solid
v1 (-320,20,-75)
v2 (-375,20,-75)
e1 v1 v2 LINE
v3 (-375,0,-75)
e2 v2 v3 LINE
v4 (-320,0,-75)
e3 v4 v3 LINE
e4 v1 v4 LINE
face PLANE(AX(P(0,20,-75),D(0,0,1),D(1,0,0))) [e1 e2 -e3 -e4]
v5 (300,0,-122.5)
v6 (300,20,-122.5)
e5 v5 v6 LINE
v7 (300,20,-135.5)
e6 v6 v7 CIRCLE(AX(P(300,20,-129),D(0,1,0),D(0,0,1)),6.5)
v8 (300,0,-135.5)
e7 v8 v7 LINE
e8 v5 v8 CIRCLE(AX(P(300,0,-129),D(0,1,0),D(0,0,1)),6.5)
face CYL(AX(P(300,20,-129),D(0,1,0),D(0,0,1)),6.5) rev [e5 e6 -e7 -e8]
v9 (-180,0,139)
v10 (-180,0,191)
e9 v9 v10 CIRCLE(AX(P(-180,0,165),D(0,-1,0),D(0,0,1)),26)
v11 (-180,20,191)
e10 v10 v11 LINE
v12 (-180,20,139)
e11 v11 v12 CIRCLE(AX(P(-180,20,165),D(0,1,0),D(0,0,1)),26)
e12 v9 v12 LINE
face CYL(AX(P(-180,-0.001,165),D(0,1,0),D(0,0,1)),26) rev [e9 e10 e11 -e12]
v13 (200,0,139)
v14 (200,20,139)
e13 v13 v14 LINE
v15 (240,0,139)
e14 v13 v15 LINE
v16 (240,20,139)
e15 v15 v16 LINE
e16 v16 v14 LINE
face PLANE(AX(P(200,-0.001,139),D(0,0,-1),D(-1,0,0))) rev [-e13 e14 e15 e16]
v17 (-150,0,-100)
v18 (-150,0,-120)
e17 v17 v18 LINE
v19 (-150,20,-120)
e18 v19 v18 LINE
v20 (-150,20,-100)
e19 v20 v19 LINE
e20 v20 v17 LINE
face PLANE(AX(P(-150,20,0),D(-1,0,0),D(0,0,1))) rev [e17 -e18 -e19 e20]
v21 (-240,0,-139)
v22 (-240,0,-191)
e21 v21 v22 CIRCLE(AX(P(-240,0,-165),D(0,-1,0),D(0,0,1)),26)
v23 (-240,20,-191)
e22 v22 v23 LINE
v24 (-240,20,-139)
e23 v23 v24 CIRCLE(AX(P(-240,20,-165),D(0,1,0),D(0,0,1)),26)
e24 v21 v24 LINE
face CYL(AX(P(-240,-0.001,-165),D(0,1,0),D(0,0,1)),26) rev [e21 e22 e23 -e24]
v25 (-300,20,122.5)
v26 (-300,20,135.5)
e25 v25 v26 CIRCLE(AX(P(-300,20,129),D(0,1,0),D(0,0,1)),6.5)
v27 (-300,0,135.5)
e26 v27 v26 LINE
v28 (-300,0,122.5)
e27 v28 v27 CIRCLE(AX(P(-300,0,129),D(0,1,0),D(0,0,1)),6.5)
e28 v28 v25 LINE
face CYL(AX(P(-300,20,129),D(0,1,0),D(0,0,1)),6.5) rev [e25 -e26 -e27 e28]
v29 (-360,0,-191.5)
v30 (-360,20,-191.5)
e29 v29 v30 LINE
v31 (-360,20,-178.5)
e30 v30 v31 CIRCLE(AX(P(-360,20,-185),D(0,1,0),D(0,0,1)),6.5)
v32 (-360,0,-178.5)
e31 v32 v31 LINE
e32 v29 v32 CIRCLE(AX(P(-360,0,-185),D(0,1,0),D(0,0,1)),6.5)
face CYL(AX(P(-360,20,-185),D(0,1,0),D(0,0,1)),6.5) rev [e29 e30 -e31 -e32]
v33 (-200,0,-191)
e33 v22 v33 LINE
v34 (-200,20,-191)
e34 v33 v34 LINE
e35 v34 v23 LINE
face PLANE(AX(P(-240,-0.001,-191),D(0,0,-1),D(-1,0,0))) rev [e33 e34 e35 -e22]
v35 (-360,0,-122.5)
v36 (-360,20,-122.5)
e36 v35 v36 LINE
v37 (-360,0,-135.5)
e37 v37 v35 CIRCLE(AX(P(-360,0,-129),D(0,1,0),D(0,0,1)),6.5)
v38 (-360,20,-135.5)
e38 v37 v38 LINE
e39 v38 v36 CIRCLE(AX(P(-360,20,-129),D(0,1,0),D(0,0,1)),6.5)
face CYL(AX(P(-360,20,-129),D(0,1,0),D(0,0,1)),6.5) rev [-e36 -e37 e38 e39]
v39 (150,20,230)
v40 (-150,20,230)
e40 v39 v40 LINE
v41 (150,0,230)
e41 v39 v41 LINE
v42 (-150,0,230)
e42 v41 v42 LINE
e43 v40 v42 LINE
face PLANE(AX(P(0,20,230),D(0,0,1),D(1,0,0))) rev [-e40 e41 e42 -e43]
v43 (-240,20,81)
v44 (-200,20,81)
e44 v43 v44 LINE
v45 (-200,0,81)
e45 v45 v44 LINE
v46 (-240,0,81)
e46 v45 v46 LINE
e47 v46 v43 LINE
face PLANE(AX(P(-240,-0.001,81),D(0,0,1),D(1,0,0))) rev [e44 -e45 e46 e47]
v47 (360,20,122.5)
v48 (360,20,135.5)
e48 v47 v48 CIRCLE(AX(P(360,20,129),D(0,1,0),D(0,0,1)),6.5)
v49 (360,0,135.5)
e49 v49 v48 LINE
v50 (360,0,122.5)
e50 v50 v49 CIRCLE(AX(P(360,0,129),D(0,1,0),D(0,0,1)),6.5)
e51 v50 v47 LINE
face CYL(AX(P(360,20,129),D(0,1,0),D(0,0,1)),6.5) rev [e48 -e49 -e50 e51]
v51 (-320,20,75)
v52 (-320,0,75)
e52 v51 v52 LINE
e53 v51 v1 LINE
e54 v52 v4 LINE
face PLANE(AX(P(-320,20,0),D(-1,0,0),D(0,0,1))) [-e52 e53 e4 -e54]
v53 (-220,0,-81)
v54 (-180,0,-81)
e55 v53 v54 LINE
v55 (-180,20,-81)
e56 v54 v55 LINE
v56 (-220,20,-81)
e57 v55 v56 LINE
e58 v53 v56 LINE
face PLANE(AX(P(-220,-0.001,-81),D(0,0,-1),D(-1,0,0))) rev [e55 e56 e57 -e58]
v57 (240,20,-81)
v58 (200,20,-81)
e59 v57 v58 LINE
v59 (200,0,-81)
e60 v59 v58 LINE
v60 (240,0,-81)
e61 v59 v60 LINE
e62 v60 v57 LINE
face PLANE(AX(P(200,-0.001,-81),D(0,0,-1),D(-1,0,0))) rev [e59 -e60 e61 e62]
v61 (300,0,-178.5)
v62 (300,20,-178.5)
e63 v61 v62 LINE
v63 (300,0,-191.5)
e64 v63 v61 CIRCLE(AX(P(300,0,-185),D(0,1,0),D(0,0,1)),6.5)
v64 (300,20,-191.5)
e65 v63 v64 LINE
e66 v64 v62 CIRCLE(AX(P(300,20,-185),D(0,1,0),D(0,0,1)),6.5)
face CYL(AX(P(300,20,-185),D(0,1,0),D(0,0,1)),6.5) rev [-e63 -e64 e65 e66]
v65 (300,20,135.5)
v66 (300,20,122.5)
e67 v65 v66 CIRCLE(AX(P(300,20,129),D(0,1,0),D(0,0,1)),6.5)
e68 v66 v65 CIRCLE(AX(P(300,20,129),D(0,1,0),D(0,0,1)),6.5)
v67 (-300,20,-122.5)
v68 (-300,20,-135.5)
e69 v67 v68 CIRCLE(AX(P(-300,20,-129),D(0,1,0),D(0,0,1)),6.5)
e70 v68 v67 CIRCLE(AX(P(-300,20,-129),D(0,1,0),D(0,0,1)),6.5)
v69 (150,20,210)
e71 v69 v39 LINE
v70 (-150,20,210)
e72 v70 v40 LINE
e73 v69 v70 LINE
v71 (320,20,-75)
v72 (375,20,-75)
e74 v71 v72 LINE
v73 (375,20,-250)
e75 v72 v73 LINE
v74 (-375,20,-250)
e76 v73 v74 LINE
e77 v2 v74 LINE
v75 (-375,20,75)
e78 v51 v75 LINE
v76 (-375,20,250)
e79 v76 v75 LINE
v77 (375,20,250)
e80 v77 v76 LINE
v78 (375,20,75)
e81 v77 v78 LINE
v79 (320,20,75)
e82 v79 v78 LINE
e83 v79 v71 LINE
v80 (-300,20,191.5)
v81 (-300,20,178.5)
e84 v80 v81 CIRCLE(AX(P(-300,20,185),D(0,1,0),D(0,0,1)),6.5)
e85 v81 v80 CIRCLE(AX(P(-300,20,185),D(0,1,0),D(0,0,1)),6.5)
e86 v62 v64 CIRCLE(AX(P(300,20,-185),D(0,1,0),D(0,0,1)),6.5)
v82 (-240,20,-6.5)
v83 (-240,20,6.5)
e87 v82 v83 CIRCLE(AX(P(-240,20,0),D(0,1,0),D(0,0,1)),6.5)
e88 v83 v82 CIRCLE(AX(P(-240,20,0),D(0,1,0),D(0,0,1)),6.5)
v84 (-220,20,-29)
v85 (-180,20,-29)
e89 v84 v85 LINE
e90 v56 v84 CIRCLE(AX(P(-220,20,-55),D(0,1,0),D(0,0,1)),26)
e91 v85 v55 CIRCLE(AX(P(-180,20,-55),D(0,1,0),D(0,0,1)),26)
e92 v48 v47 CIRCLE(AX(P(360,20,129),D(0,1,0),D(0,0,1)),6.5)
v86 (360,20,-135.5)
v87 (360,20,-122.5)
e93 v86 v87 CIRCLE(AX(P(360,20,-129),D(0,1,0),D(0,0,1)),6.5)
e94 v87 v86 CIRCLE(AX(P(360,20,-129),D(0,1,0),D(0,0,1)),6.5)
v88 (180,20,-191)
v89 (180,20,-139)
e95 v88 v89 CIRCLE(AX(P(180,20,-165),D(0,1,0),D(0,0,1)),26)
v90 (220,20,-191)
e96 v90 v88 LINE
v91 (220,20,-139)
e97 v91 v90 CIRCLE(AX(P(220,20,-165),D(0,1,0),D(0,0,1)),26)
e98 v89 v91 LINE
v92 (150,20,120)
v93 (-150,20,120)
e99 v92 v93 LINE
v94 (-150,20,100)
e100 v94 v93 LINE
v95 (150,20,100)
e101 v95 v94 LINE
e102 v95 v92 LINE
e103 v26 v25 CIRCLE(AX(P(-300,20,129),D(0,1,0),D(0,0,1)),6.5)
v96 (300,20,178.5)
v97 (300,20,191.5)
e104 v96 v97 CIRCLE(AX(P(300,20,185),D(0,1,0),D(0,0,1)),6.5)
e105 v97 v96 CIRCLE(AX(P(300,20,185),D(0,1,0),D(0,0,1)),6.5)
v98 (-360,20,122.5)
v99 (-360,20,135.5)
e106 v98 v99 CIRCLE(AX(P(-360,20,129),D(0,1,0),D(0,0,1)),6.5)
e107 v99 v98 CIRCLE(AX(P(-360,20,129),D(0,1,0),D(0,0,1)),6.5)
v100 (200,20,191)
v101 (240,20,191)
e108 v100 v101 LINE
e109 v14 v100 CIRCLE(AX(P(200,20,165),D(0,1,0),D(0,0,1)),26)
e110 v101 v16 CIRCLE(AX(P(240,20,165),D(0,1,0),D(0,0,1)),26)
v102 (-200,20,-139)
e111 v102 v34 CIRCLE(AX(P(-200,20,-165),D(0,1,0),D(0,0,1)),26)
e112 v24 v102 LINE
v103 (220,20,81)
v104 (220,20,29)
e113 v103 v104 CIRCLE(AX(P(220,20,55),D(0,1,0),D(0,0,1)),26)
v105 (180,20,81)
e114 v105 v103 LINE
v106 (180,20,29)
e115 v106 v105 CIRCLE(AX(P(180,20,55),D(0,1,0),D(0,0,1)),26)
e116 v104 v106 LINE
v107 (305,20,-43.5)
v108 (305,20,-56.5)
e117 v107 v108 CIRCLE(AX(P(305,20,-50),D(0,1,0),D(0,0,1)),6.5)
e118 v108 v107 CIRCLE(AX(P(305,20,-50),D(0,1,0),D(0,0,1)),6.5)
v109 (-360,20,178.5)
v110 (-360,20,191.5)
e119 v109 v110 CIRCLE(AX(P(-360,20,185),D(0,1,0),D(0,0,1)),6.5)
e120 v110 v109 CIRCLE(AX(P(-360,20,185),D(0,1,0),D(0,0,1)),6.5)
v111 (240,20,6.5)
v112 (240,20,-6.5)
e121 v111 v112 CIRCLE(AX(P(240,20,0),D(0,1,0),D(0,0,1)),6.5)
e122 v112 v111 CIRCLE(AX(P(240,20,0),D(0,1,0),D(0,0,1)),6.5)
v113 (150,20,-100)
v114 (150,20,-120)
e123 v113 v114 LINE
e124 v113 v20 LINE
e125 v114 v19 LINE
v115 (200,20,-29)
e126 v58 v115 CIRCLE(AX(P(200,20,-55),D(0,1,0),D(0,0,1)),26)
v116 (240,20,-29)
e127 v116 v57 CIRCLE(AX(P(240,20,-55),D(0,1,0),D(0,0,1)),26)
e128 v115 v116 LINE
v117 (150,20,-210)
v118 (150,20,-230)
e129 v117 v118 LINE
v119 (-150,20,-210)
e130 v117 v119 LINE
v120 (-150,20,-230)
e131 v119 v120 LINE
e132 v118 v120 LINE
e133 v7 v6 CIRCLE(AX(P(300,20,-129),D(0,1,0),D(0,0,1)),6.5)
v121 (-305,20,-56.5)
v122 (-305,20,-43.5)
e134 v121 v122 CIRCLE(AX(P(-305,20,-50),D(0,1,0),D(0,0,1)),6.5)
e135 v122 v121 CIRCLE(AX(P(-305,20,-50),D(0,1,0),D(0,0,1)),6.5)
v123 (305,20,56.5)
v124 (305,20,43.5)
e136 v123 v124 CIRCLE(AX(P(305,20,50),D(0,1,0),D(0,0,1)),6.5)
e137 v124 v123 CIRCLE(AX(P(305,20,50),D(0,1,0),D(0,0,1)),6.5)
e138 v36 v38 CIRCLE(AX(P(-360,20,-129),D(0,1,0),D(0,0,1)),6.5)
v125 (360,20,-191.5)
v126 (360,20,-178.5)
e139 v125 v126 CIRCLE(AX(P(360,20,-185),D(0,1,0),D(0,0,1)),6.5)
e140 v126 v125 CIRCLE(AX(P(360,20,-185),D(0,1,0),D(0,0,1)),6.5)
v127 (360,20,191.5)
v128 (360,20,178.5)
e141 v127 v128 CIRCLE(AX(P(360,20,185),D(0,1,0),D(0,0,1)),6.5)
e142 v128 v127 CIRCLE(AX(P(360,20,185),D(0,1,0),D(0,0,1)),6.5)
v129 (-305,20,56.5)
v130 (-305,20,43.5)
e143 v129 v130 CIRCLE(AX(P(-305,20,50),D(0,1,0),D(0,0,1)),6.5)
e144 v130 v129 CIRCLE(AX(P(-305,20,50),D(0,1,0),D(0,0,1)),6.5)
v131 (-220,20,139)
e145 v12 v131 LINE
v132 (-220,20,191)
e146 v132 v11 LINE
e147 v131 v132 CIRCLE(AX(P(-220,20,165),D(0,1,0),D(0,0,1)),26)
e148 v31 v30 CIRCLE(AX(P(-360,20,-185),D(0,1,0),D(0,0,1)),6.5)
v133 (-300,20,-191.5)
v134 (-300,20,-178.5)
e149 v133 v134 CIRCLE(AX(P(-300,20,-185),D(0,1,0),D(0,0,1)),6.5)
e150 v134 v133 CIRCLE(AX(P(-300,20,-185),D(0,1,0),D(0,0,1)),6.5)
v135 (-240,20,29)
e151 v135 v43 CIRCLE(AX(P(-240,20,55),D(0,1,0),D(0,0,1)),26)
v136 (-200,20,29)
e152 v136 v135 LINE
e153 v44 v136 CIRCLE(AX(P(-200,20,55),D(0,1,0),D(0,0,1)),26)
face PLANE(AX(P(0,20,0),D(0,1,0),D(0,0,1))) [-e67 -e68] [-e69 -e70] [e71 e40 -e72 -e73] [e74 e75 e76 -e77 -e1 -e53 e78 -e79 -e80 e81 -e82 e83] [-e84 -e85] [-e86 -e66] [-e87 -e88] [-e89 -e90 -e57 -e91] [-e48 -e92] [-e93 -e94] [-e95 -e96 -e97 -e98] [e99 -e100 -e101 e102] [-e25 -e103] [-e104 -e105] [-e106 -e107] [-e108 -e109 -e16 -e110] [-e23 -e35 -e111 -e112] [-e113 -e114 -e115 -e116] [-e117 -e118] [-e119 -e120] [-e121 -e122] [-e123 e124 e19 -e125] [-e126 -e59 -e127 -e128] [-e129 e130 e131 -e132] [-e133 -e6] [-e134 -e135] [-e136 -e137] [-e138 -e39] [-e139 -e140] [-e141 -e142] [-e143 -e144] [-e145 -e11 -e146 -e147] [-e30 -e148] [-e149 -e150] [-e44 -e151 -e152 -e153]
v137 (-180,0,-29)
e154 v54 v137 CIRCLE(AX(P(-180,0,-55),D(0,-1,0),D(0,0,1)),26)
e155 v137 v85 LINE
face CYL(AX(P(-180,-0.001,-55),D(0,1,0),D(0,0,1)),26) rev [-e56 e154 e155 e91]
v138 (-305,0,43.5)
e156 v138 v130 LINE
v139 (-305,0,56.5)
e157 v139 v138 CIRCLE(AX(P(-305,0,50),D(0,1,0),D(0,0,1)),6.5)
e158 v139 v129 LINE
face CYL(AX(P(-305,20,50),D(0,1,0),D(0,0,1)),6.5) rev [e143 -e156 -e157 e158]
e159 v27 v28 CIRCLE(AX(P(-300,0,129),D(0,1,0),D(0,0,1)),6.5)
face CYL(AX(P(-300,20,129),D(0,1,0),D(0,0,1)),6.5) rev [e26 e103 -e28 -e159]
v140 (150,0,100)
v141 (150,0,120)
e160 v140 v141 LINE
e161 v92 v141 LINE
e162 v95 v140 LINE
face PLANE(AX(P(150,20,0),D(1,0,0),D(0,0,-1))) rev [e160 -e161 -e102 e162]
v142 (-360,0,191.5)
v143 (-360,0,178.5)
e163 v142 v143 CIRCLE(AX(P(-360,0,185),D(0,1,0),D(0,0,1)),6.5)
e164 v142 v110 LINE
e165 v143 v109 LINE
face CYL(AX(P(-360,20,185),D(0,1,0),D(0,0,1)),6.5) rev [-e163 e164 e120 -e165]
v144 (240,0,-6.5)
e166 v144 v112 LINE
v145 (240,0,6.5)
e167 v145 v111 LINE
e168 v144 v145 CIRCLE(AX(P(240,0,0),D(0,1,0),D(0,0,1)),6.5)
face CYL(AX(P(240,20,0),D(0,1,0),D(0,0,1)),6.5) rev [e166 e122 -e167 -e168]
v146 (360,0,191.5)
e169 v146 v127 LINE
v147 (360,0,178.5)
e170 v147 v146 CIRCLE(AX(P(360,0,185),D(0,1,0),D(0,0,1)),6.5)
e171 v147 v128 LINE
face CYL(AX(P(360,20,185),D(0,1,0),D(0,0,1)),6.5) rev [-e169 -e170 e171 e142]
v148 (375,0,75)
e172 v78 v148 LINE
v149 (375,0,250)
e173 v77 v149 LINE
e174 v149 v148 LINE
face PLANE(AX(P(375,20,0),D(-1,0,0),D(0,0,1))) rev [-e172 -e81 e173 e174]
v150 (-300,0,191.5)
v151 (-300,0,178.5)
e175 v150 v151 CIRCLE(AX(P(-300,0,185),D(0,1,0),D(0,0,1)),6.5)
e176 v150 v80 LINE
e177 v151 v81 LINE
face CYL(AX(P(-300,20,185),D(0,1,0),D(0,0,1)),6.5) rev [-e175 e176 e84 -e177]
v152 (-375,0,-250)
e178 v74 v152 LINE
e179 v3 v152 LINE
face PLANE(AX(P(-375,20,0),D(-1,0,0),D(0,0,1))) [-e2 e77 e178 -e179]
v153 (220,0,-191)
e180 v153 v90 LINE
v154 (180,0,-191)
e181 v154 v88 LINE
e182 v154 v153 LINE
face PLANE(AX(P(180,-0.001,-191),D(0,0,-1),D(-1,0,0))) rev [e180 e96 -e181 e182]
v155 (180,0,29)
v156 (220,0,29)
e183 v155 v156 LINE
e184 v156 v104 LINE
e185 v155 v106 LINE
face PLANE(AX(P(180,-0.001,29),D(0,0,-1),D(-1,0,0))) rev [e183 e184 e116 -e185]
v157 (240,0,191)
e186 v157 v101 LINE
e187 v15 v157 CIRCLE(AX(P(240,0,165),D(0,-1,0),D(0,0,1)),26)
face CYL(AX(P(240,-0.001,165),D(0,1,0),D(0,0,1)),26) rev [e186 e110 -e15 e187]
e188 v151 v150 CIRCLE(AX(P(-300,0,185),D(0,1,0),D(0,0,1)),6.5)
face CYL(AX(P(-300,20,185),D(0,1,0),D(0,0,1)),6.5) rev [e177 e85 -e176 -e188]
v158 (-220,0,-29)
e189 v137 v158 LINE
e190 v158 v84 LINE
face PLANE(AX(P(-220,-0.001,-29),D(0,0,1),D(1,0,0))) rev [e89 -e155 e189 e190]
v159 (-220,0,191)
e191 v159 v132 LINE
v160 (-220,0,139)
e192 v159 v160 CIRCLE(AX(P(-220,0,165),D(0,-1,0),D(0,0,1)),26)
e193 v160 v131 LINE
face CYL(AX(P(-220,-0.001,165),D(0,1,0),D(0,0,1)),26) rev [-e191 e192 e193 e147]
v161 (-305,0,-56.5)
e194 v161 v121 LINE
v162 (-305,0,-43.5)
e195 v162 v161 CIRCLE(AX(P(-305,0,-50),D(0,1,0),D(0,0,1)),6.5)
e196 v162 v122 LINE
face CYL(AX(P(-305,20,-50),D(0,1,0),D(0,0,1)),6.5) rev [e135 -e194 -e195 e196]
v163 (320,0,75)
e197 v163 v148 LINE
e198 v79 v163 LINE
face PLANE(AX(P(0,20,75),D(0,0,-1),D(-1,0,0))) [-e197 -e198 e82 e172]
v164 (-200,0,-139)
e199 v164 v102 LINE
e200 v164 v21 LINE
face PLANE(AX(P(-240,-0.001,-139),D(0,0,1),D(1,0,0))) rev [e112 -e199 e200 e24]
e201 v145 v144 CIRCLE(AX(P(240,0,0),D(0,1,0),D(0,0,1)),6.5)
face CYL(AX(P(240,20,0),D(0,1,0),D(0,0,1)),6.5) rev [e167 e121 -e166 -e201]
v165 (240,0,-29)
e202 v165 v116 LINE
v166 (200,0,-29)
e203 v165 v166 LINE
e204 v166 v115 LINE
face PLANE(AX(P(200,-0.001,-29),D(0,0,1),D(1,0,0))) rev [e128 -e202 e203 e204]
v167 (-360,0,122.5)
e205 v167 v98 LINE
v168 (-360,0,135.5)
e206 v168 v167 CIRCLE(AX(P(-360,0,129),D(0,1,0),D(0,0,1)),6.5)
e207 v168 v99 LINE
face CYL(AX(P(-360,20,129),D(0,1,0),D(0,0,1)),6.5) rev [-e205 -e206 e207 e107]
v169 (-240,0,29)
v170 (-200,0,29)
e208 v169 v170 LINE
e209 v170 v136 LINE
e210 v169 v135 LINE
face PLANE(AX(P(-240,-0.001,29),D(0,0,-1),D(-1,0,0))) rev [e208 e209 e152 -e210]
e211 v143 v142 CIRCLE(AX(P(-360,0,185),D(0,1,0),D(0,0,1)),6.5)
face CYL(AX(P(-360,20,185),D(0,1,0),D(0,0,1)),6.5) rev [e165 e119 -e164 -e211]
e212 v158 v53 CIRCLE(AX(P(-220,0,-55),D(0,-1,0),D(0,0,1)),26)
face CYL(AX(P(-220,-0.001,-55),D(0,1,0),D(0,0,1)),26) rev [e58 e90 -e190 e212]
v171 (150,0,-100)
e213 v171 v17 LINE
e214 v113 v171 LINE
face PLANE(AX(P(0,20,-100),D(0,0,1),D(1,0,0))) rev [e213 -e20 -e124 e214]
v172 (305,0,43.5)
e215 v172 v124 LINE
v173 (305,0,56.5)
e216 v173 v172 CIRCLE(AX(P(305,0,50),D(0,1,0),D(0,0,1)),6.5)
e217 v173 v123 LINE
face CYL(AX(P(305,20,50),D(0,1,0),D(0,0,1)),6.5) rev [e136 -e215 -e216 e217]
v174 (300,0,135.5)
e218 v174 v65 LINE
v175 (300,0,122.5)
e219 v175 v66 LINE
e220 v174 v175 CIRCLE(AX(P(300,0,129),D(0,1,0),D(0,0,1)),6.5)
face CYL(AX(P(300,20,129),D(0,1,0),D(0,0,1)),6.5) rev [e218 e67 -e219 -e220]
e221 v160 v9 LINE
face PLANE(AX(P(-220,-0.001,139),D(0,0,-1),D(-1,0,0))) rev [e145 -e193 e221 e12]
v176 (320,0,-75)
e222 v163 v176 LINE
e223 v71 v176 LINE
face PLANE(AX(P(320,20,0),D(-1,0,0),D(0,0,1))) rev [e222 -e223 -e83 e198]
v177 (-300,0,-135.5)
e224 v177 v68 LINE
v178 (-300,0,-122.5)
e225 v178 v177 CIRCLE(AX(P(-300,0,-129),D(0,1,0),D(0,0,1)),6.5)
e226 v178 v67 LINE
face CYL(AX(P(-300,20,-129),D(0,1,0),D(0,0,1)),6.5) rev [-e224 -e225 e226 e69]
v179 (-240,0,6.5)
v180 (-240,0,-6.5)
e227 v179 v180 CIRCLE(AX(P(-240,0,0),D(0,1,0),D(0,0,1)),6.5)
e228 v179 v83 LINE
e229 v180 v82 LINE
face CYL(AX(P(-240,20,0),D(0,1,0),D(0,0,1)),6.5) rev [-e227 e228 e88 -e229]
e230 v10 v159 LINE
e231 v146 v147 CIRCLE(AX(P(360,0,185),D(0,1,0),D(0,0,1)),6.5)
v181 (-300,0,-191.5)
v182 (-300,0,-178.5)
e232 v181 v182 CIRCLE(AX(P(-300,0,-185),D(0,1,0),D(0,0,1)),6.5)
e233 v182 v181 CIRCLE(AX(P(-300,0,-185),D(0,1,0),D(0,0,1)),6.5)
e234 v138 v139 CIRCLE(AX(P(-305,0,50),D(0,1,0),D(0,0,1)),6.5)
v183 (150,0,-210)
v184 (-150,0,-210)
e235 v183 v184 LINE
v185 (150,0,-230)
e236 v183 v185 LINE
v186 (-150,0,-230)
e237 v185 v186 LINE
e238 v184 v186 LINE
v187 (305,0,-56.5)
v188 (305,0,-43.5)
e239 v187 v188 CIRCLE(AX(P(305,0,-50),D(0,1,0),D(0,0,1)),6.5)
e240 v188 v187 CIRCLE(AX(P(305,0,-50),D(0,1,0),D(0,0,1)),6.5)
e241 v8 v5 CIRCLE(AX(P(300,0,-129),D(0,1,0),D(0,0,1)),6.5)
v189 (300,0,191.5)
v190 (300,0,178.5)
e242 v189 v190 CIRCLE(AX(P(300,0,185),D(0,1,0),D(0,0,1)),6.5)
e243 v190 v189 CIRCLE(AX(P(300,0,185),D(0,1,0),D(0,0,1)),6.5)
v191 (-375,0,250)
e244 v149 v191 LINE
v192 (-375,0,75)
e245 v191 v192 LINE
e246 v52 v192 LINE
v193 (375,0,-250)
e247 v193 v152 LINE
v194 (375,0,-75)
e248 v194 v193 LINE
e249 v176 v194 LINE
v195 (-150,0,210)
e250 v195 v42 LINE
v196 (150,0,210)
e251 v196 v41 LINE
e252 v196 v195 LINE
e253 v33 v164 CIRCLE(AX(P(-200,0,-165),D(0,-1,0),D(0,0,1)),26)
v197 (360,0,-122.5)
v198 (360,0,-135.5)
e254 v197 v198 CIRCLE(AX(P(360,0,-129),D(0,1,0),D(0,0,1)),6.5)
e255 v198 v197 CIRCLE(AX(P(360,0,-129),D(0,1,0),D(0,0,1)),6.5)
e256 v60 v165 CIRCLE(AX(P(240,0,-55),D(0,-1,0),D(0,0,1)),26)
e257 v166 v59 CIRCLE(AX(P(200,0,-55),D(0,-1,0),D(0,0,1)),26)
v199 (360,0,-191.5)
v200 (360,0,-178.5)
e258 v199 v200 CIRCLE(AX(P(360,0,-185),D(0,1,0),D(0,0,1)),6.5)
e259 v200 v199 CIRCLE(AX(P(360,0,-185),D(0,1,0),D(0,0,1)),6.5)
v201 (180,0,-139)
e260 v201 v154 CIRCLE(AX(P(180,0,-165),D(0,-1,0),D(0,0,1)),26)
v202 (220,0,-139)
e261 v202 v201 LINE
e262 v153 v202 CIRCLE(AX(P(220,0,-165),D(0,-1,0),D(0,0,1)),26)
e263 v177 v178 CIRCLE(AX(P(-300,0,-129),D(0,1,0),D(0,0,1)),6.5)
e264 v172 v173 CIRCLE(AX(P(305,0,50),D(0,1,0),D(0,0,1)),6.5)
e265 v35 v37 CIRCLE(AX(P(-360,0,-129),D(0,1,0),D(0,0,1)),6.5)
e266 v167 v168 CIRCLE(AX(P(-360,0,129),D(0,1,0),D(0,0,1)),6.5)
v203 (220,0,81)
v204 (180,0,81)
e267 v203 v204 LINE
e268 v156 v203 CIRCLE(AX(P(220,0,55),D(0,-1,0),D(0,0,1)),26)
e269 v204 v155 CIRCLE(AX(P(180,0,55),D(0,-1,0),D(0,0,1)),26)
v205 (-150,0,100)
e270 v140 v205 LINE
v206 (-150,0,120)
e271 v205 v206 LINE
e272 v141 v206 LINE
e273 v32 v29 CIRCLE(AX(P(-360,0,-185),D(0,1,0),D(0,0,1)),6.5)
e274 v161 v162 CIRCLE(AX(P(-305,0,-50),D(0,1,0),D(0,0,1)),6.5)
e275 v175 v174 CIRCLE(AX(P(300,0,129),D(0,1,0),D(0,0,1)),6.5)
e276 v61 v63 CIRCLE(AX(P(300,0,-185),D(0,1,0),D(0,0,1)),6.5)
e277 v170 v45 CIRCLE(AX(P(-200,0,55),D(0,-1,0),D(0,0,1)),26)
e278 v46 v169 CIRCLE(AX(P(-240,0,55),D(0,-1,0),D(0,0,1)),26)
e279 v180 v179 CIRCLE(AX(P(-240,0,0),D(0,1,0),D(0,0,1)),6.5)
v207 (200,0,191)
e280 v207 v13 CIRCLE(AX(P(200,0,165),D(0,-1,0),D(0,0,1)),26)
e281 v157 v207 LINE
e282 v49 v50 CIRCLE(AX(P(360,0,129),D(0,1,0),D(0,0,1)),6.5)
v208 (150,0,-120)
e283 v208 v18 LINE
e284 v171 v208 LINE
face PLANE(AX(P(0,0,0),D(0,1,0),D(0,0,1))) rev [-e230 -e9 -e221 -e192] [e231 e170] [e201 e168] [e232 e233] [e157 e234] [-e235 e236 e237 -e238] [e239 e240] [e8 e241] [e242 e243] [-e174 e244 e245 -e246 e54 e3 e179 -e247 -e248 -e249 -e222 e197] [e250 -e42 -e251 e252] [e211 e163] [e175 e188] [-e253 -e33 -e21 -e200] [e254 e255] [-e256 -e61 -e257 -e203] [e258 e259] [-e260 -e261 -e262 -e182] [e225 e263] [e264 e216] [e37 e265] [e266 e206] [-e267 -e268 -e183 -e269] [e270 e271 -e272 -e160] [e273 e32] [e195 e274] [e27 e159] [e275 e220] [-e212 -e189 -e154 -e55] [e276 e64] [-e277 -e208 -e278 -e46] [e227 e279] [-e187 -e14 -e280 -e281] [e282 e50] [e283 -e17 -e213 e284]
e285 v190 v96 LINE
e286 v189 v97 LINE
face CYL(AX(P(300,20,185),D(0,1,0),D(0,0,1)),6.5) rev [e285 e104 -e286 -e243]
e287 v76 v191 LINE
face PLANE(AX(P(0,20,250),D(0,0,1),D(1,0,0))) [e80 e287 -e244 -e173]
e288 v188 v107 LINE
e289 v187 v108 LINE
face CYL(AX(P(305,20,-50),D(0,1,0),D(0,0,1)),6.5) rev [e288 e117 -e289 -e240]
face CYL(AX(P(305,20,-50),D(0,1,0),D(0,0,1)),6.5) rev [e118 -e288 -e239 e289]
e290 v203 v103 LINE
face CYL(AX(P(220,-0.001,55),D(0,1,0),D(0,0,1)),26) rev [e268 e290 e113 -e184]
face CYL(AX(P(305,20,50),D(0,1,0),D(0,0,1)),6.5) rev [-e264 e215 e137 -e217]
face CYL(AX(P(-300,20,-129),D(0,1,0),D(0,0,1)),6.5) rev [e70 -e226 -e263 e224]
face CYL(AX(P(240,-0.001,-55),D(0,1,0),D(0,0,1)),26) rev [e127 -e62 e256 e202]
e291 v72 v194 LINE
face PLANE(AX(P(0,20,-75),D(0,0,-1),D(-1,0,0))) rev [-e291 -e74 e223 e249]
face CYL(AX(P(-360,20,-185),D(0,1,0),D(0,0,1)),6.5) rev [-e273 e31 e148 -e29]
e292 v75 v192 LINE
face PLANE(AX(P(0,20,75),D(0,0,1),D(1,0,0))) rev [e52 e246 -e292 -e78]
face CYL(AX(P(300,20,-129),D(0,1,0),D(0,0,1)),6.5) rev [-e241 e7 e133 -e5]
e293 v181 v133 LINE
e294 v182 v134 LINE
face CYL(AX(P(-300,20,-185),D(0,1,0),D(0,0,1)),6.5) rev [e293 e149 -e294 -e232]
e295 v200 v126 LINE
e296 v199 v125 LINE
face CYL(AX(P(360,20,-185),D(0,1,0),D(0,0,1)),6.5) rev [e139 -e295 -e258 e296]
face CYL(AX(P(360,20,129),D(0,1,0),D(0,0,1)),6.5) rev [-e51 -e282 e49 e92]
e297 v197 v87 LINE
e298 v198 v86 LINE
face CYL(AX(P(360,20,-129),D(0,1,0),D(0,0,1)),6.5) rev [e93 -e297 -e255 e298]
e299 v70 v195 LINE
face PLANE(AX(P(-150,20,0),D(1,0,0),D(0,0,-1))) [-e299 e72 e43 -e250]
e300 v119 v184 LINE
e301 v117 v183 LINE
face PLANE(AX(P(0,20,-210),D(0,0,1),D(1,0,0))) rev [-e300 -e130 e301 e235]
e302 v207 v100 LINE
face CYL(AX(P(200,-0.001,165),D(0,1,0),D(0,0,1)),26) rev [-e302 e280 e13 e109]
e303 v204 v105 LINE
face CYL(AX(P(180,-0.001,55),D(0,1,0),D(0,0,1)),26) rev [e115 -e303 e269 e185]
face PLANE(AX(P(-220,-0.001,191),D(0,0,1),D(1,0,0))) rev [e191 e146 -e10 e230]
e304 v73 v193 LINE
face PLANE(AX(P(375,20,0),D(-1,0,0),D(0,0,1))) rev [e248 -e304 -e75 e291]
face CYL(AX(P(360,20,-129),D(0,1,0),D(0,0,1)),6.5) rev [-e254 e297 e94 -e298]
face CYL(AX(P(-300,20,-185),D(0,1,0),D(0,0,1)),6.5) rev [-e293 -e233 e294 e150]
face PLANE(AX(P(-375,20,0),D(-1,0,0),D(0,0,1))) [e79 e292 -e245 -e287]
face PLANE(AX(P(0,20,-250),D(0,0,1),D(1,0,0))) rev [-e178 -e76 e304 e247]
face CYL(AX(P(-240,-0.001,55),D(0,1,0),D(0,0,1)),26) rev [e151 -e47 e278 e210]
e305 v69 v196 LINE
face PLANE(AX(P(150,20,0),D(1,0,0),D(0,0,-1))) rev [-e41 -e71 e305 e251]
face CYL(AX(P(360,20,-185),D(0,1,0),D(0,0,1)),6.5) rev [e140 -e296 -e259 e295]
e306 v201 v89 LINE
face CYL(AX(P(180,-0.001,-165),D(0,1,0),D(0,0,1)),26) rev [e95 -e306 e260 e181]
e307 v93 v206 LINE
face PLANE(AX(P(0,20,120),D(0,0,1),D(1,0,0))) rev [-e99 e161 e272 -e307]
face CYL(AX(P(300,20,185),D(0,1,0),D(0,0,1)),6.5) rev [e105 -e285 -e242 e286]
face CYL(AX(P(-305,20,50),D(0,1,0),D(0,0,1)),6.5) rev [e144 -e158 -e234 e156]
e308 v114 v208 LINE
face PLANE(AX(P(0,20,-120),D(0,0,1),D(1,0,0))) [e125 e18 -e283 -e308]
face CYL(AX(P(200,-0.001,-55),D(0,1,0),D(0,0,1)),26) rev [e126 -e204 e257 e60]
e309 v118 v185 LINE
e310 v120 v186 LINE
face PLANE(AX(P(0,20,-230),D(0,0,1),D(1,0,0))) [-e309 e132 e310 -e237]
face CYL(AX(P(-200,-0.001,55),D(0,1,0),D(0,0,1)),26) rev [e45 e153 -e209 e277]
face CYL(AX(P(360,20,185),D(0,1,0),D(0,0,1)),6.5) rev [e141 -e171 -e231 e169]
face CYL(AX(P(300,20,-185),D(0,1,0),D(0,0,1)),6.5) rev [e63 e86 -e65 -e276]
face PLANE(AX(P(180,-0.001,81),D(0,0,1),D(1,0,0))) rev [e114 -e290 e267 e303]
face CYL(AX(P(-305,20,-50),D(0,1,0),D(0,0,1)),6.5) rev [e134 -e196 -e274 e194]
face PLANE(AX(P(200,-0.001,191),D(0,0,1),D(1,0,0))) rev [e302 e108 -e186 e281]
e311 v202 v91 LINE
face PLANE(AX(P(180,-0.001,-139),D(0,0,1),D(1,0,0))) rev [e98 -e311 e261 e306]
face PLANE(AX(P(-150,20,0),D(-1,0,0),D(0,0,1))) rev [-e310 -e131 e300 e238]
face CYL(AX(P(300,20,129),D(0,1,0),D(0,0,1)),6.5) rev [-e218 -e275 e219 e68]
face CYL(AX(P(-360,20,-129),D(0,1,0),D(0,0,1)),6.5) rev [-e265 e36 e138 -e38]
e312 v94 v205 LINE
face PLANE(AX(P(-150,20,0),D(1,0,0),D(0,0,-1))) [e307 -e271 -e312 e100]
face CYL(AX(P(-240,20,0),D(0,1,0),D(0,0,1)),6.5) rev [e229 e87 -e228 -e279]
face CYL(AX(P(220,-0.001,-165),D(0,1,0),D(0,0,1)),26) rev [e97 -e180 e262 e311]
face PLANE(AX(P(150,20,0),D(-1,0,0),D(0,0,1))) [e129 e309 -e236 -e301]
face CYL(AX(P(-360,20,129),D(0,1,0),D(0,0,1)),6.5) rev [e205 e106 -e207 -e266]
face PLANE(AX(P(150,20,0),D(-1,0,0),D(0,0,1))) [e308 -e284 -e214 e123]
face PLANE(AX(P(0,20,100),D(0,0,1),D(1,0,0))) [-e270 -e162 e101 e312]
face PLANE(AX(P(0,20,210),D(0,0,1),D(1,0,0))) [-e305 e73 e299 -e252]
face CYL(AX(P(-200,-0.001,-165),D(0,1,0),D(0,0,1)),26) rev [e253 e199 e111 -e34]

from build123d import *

# Parameters (mm, degrees)
SKETCH1_W                  = 300
SKETCH1_H                  = 20
BOSS_EXTRUDE1_DEPTH        = 20
F_13_0_13_DIAMETER_HOLE1_D = 13
CUT_EXTRUDE1_REACH         = 453.137


with BuildPart() as part:
    # Sketch1 → Boss-Extrude1 (new body)
    with BuildSketch(Plane(origin=(0, 0, 0), x_dir=(1, 0, 0), z_dir=(0, 1, 0))):
        Polygon((-375, -250), (375, -250), (375, -75), (320, -75), (320, 75), (375, 75), (375, 250), (-375, 250), (-375, 75), (-320, 75), (-320, -75), (-375, -75), align=None)
        with Locations((0, -220)):
            Rectangle(SKETCH1_W, SKETCH1_H, mode=Mode.SUBTRACT)
        with Locations((0, -110)):
            Rectangle(SKETCH1_W, SKETCH1_H, mode=Mode.SUBTRACT)
        with Locations((0, 110)):
            Rectangle(SKETCH1_W, SKETCH1_H, mode=Mode.SUBTRACT)
        with Locations((0, 220)):
            Rectangle(SKETCH1_W, SKETCH1_H, mode=Mode.SUBTRACT)
    extrude(amount=BOSS_EXTRUDE1_DEPTH)

    # Ø13.0 (13) Diameter Hole1 (through all)
    with Locations(Plane(origin=(0, 20, 0), x_dir=(1, 0, 0), z_dir=(0, 1, 0))):
        with Locations((-360, 129), (-305, 50), (-240, 0), (-300, 129), (-300, 185), (-360, 185), (-360, -129), (-360, -185), (-300, -129), (-300, -185), (-305, -50), (360, -129), (300, -129), (360, -185), (360, 129), (360, 185), (300, 129), (305, -50), (300, -185), (300, 185), (240, 0), (305, 50)):
            Hole(F_13_0_13_DIAMETER_HOLE1_D / 2)

    # Sketch4 → Cut-Extrude1 (cut, up to next)
    with BuildSketch(Plane(origin=(0, 20, 0), x_dir=(1, 0, 0), z_dir=(0, 1, 0)), mode=Mode.PRIVATE) as cut_extrude1_sk1:
        with BuildLine():
            Line((-240, 191), (-200, 191))
            ThreePointArc((-200, 191), (-174, 165), (-200, 139))
            Line((-200, 139), (-240, 139))
            ThreePointArc((-240, 139), (-266, 165), (-240, 191))
        make_face()
    cut_extrude1_tool1 = extrude(cut_extrude1_sk1.sketch, amount=-CUT_EXTRUDE1_REACH, mode=Mode.PRIVATE) & part.part
    # Sketch4 → Cut-Extrude1 (cut, up to next)
    with BuildSketch(Plane(origin=(0, 20, 0), x_dir=(1, 0, 0), z_dir=(0, 1, 0)), mode=Mode.PRIVATE) as cut_extrude1_sk2:
        with BuildLine():
            Line((-220, 81), (-180, 81))
            ThreePointArc((-180, 81), (-154, 55), (-180, 29))
            Line((-180, 29), (-220, 29))
            ThreePointArc((-220, 29), (-246, 55), (-220, 81))
        make_face()
    cut_extrude1_tool2 = extrude(cut_extrude1_sk2.sketch, amount=-CUT_EXTRUDE1_REACH, mode=Mode.PRIVATE) & part.part
    # Sketch4 → Cut-Extrude1 (cut, up to next)
    with BuildSketch(Plane(origin=(0, 20, 0), x_dir=(1, 0, 0), z_dir=(0, 1, 0)), mode=Mode.PRIVATE) as cut_extrude1_sk3:
        with BuildLine():
            Line((180, 191), (220, 191))
            ThreePointArc((220, 191), (246, 165), (220, 139))
            Line((220, 139), (180, 139))
            ThreePointArc((180, 139), (154, 165), (180, 191))
        make_face()
    cut_extrude1_tool3 = extrude(cut_extrude1_sk3.sketch, amount=-CUT_EXTRUDE1_REACH, mode=Mode.PRIVATE) & part.part
    # Sketch4 → Cut-Extrude1 (cut, up to next)
    with BuildSketch(Plane(origin=(0, 20, 0), x_dir=(1, 0, 0), z_dir=(0, 1, 0)), mode=Mode.PRIVATE) as cut_extrude1_sk4:
        with BuildLine():
            Line((200, 81), (240, 81))
            ThreePointArc((240, 81), (266, 55), (240, 29))
            Line((240, 29), (200, 29))
            ThreePointArc((200, 29), (174, 55), (200, 81))
        make_face()
    cut_extrude1_tool4 = extrude(cut_extrude1_sk4.sketch, amount=-CUT_EXTRUDE1_REACH, mode=Mode.PRIVATE) & part.part
    # Sketch4 → Cut-Extrude1 (cut, up to next)
    with BuildSketch(Plane(origin=(0, 20, 0), x_dir=(1, 0, 0), z_dir=(0, 1, 0)), mode=Mode.PRIVATE) as cut_extrude1_sk5:
        with BuildLine():
            Line((180, -29), (220, -29))
            ThreePointArc((220, -29), (246, -55), (220, -81))
            Line((220, -81), (180, -81))
            ThreePointArc((180, -81), (154, -55), (180, -29))
        make_face()
    cut_extrude1_tool5 = extrude(cut_extrude1_sk5.sketch, amount=-CUT_EXTRUDE1_REACH, mode=Mode.PRIVATE) & part.part
    # Sketch4 → Cut-Extrude1 (cut, up to next)
    with BuildSketch(Plane(origin=(0, 20, 0), x_dir=(1, 0, 0), z_dir=(0, 1, 0)), mode=Mode.PRIVATE) as cut_extrude1_sk6:
        with BuildLine():
            Line((200, -139), (240, -139))
            ThreePointArc((240, -139), (266, -165), (240, -191))
            Line((240, -191), (200, -191))
            ThreePointArc((200, -191), (174, -165), (200, -139))
        make_face()
    cut_extrude1_tool6 = extrude(cut_extrude1_sk6.sketch, amount=-CUT_EXTRUDE1_REACH, mode=Mode.PRIVATE) & part.part
    # Sketch4 → Cut-Extrude1 (cut, up to next)
    with BuildSketch(Plane(origin=(0, 20, 0), x_dir=(1, 0, 0), z_dir=(0, 1, 0)), mode=Mode.PRIVATE) as cut_extrude1_sk7:
        with BuildLine():
            Line((-240, -29), (-200, -29))
            ThreePointArc((-200, -29), (-174, -55), (-200, -81))
            Line((-200, -81), (-240, -81))
            ThreePointArc((-240, -81), (-266, -55), (-240, -29))
        make_face()
    cut_extrude1_tool7 = extrude(cut_extrude1_sk7.sketch, amount=-CUT_EXTRUDE1_REACH, mode=Mode.PRIVATE) & part.part
    # Sketch4 → Cut-Extrude1 (cut, up to next)
    with BuildSketch(Plane(origin=(0, 20, 0), x_dir=(1, 0, 0), z_dir=(0, 1, 0)), mode=Mode.PRIVATE) as cut_extrude1_sk8:
        with BuildLine():
            Line((-220, -139), (-180, -139))
            ThreePointArc((-180, -139), (-154, -165), (-180, -191))
            Line((-180, -191), (-220, -191))
            ThreePointArc((-220, -191), (-246, -165), (-220, -139))
        make_face()
    cut_extrude1_tool8 = extrude(cut_extrude1_sk8.sketch, amount=-CUT_EXTRUDE1_REACH, mode=Mode.PRIVATE) & part.part
    add(cut_extrude1_tool1.solids().sort_by_distance((-220, 20, -165))[0], mode=Mode.SUBTRACT)
    add(cut_extrude1_tool2.solids().sort_by_distance((-200, 20, -55))[0], mode=Mode.SUBTRACT)
    add(cut_extrude1_tool3.solids().sort_by_distance((200, 20, -165))[0], mode=Mode.SUBTRACT)
    add(cut_extrude1_tool4.solids().sort_by_distance((220, 20, -55))[0], mode=Mode.SUBTRACT)
    add(cut_extrude1_tool5.solids().sort_by_distance((200, 20, 55))[0], mode=Mode.SUBTRACT)
    add(cut_extrude1_tool6.solids().sort_by_distance((220, 20, 165))[0], mode=Mode.SUBTRACT)
    add(cut_extrude1_tool7.solids().sort_by_distance((-220, 20, 55))[0], mode=Mode.SUBTRACT)
    add(cut_extrude1_tool8.solids().sort_by_distance((-200, 20, 165))[0], mode=Mode.SUBTRACT)


solid = part.part
